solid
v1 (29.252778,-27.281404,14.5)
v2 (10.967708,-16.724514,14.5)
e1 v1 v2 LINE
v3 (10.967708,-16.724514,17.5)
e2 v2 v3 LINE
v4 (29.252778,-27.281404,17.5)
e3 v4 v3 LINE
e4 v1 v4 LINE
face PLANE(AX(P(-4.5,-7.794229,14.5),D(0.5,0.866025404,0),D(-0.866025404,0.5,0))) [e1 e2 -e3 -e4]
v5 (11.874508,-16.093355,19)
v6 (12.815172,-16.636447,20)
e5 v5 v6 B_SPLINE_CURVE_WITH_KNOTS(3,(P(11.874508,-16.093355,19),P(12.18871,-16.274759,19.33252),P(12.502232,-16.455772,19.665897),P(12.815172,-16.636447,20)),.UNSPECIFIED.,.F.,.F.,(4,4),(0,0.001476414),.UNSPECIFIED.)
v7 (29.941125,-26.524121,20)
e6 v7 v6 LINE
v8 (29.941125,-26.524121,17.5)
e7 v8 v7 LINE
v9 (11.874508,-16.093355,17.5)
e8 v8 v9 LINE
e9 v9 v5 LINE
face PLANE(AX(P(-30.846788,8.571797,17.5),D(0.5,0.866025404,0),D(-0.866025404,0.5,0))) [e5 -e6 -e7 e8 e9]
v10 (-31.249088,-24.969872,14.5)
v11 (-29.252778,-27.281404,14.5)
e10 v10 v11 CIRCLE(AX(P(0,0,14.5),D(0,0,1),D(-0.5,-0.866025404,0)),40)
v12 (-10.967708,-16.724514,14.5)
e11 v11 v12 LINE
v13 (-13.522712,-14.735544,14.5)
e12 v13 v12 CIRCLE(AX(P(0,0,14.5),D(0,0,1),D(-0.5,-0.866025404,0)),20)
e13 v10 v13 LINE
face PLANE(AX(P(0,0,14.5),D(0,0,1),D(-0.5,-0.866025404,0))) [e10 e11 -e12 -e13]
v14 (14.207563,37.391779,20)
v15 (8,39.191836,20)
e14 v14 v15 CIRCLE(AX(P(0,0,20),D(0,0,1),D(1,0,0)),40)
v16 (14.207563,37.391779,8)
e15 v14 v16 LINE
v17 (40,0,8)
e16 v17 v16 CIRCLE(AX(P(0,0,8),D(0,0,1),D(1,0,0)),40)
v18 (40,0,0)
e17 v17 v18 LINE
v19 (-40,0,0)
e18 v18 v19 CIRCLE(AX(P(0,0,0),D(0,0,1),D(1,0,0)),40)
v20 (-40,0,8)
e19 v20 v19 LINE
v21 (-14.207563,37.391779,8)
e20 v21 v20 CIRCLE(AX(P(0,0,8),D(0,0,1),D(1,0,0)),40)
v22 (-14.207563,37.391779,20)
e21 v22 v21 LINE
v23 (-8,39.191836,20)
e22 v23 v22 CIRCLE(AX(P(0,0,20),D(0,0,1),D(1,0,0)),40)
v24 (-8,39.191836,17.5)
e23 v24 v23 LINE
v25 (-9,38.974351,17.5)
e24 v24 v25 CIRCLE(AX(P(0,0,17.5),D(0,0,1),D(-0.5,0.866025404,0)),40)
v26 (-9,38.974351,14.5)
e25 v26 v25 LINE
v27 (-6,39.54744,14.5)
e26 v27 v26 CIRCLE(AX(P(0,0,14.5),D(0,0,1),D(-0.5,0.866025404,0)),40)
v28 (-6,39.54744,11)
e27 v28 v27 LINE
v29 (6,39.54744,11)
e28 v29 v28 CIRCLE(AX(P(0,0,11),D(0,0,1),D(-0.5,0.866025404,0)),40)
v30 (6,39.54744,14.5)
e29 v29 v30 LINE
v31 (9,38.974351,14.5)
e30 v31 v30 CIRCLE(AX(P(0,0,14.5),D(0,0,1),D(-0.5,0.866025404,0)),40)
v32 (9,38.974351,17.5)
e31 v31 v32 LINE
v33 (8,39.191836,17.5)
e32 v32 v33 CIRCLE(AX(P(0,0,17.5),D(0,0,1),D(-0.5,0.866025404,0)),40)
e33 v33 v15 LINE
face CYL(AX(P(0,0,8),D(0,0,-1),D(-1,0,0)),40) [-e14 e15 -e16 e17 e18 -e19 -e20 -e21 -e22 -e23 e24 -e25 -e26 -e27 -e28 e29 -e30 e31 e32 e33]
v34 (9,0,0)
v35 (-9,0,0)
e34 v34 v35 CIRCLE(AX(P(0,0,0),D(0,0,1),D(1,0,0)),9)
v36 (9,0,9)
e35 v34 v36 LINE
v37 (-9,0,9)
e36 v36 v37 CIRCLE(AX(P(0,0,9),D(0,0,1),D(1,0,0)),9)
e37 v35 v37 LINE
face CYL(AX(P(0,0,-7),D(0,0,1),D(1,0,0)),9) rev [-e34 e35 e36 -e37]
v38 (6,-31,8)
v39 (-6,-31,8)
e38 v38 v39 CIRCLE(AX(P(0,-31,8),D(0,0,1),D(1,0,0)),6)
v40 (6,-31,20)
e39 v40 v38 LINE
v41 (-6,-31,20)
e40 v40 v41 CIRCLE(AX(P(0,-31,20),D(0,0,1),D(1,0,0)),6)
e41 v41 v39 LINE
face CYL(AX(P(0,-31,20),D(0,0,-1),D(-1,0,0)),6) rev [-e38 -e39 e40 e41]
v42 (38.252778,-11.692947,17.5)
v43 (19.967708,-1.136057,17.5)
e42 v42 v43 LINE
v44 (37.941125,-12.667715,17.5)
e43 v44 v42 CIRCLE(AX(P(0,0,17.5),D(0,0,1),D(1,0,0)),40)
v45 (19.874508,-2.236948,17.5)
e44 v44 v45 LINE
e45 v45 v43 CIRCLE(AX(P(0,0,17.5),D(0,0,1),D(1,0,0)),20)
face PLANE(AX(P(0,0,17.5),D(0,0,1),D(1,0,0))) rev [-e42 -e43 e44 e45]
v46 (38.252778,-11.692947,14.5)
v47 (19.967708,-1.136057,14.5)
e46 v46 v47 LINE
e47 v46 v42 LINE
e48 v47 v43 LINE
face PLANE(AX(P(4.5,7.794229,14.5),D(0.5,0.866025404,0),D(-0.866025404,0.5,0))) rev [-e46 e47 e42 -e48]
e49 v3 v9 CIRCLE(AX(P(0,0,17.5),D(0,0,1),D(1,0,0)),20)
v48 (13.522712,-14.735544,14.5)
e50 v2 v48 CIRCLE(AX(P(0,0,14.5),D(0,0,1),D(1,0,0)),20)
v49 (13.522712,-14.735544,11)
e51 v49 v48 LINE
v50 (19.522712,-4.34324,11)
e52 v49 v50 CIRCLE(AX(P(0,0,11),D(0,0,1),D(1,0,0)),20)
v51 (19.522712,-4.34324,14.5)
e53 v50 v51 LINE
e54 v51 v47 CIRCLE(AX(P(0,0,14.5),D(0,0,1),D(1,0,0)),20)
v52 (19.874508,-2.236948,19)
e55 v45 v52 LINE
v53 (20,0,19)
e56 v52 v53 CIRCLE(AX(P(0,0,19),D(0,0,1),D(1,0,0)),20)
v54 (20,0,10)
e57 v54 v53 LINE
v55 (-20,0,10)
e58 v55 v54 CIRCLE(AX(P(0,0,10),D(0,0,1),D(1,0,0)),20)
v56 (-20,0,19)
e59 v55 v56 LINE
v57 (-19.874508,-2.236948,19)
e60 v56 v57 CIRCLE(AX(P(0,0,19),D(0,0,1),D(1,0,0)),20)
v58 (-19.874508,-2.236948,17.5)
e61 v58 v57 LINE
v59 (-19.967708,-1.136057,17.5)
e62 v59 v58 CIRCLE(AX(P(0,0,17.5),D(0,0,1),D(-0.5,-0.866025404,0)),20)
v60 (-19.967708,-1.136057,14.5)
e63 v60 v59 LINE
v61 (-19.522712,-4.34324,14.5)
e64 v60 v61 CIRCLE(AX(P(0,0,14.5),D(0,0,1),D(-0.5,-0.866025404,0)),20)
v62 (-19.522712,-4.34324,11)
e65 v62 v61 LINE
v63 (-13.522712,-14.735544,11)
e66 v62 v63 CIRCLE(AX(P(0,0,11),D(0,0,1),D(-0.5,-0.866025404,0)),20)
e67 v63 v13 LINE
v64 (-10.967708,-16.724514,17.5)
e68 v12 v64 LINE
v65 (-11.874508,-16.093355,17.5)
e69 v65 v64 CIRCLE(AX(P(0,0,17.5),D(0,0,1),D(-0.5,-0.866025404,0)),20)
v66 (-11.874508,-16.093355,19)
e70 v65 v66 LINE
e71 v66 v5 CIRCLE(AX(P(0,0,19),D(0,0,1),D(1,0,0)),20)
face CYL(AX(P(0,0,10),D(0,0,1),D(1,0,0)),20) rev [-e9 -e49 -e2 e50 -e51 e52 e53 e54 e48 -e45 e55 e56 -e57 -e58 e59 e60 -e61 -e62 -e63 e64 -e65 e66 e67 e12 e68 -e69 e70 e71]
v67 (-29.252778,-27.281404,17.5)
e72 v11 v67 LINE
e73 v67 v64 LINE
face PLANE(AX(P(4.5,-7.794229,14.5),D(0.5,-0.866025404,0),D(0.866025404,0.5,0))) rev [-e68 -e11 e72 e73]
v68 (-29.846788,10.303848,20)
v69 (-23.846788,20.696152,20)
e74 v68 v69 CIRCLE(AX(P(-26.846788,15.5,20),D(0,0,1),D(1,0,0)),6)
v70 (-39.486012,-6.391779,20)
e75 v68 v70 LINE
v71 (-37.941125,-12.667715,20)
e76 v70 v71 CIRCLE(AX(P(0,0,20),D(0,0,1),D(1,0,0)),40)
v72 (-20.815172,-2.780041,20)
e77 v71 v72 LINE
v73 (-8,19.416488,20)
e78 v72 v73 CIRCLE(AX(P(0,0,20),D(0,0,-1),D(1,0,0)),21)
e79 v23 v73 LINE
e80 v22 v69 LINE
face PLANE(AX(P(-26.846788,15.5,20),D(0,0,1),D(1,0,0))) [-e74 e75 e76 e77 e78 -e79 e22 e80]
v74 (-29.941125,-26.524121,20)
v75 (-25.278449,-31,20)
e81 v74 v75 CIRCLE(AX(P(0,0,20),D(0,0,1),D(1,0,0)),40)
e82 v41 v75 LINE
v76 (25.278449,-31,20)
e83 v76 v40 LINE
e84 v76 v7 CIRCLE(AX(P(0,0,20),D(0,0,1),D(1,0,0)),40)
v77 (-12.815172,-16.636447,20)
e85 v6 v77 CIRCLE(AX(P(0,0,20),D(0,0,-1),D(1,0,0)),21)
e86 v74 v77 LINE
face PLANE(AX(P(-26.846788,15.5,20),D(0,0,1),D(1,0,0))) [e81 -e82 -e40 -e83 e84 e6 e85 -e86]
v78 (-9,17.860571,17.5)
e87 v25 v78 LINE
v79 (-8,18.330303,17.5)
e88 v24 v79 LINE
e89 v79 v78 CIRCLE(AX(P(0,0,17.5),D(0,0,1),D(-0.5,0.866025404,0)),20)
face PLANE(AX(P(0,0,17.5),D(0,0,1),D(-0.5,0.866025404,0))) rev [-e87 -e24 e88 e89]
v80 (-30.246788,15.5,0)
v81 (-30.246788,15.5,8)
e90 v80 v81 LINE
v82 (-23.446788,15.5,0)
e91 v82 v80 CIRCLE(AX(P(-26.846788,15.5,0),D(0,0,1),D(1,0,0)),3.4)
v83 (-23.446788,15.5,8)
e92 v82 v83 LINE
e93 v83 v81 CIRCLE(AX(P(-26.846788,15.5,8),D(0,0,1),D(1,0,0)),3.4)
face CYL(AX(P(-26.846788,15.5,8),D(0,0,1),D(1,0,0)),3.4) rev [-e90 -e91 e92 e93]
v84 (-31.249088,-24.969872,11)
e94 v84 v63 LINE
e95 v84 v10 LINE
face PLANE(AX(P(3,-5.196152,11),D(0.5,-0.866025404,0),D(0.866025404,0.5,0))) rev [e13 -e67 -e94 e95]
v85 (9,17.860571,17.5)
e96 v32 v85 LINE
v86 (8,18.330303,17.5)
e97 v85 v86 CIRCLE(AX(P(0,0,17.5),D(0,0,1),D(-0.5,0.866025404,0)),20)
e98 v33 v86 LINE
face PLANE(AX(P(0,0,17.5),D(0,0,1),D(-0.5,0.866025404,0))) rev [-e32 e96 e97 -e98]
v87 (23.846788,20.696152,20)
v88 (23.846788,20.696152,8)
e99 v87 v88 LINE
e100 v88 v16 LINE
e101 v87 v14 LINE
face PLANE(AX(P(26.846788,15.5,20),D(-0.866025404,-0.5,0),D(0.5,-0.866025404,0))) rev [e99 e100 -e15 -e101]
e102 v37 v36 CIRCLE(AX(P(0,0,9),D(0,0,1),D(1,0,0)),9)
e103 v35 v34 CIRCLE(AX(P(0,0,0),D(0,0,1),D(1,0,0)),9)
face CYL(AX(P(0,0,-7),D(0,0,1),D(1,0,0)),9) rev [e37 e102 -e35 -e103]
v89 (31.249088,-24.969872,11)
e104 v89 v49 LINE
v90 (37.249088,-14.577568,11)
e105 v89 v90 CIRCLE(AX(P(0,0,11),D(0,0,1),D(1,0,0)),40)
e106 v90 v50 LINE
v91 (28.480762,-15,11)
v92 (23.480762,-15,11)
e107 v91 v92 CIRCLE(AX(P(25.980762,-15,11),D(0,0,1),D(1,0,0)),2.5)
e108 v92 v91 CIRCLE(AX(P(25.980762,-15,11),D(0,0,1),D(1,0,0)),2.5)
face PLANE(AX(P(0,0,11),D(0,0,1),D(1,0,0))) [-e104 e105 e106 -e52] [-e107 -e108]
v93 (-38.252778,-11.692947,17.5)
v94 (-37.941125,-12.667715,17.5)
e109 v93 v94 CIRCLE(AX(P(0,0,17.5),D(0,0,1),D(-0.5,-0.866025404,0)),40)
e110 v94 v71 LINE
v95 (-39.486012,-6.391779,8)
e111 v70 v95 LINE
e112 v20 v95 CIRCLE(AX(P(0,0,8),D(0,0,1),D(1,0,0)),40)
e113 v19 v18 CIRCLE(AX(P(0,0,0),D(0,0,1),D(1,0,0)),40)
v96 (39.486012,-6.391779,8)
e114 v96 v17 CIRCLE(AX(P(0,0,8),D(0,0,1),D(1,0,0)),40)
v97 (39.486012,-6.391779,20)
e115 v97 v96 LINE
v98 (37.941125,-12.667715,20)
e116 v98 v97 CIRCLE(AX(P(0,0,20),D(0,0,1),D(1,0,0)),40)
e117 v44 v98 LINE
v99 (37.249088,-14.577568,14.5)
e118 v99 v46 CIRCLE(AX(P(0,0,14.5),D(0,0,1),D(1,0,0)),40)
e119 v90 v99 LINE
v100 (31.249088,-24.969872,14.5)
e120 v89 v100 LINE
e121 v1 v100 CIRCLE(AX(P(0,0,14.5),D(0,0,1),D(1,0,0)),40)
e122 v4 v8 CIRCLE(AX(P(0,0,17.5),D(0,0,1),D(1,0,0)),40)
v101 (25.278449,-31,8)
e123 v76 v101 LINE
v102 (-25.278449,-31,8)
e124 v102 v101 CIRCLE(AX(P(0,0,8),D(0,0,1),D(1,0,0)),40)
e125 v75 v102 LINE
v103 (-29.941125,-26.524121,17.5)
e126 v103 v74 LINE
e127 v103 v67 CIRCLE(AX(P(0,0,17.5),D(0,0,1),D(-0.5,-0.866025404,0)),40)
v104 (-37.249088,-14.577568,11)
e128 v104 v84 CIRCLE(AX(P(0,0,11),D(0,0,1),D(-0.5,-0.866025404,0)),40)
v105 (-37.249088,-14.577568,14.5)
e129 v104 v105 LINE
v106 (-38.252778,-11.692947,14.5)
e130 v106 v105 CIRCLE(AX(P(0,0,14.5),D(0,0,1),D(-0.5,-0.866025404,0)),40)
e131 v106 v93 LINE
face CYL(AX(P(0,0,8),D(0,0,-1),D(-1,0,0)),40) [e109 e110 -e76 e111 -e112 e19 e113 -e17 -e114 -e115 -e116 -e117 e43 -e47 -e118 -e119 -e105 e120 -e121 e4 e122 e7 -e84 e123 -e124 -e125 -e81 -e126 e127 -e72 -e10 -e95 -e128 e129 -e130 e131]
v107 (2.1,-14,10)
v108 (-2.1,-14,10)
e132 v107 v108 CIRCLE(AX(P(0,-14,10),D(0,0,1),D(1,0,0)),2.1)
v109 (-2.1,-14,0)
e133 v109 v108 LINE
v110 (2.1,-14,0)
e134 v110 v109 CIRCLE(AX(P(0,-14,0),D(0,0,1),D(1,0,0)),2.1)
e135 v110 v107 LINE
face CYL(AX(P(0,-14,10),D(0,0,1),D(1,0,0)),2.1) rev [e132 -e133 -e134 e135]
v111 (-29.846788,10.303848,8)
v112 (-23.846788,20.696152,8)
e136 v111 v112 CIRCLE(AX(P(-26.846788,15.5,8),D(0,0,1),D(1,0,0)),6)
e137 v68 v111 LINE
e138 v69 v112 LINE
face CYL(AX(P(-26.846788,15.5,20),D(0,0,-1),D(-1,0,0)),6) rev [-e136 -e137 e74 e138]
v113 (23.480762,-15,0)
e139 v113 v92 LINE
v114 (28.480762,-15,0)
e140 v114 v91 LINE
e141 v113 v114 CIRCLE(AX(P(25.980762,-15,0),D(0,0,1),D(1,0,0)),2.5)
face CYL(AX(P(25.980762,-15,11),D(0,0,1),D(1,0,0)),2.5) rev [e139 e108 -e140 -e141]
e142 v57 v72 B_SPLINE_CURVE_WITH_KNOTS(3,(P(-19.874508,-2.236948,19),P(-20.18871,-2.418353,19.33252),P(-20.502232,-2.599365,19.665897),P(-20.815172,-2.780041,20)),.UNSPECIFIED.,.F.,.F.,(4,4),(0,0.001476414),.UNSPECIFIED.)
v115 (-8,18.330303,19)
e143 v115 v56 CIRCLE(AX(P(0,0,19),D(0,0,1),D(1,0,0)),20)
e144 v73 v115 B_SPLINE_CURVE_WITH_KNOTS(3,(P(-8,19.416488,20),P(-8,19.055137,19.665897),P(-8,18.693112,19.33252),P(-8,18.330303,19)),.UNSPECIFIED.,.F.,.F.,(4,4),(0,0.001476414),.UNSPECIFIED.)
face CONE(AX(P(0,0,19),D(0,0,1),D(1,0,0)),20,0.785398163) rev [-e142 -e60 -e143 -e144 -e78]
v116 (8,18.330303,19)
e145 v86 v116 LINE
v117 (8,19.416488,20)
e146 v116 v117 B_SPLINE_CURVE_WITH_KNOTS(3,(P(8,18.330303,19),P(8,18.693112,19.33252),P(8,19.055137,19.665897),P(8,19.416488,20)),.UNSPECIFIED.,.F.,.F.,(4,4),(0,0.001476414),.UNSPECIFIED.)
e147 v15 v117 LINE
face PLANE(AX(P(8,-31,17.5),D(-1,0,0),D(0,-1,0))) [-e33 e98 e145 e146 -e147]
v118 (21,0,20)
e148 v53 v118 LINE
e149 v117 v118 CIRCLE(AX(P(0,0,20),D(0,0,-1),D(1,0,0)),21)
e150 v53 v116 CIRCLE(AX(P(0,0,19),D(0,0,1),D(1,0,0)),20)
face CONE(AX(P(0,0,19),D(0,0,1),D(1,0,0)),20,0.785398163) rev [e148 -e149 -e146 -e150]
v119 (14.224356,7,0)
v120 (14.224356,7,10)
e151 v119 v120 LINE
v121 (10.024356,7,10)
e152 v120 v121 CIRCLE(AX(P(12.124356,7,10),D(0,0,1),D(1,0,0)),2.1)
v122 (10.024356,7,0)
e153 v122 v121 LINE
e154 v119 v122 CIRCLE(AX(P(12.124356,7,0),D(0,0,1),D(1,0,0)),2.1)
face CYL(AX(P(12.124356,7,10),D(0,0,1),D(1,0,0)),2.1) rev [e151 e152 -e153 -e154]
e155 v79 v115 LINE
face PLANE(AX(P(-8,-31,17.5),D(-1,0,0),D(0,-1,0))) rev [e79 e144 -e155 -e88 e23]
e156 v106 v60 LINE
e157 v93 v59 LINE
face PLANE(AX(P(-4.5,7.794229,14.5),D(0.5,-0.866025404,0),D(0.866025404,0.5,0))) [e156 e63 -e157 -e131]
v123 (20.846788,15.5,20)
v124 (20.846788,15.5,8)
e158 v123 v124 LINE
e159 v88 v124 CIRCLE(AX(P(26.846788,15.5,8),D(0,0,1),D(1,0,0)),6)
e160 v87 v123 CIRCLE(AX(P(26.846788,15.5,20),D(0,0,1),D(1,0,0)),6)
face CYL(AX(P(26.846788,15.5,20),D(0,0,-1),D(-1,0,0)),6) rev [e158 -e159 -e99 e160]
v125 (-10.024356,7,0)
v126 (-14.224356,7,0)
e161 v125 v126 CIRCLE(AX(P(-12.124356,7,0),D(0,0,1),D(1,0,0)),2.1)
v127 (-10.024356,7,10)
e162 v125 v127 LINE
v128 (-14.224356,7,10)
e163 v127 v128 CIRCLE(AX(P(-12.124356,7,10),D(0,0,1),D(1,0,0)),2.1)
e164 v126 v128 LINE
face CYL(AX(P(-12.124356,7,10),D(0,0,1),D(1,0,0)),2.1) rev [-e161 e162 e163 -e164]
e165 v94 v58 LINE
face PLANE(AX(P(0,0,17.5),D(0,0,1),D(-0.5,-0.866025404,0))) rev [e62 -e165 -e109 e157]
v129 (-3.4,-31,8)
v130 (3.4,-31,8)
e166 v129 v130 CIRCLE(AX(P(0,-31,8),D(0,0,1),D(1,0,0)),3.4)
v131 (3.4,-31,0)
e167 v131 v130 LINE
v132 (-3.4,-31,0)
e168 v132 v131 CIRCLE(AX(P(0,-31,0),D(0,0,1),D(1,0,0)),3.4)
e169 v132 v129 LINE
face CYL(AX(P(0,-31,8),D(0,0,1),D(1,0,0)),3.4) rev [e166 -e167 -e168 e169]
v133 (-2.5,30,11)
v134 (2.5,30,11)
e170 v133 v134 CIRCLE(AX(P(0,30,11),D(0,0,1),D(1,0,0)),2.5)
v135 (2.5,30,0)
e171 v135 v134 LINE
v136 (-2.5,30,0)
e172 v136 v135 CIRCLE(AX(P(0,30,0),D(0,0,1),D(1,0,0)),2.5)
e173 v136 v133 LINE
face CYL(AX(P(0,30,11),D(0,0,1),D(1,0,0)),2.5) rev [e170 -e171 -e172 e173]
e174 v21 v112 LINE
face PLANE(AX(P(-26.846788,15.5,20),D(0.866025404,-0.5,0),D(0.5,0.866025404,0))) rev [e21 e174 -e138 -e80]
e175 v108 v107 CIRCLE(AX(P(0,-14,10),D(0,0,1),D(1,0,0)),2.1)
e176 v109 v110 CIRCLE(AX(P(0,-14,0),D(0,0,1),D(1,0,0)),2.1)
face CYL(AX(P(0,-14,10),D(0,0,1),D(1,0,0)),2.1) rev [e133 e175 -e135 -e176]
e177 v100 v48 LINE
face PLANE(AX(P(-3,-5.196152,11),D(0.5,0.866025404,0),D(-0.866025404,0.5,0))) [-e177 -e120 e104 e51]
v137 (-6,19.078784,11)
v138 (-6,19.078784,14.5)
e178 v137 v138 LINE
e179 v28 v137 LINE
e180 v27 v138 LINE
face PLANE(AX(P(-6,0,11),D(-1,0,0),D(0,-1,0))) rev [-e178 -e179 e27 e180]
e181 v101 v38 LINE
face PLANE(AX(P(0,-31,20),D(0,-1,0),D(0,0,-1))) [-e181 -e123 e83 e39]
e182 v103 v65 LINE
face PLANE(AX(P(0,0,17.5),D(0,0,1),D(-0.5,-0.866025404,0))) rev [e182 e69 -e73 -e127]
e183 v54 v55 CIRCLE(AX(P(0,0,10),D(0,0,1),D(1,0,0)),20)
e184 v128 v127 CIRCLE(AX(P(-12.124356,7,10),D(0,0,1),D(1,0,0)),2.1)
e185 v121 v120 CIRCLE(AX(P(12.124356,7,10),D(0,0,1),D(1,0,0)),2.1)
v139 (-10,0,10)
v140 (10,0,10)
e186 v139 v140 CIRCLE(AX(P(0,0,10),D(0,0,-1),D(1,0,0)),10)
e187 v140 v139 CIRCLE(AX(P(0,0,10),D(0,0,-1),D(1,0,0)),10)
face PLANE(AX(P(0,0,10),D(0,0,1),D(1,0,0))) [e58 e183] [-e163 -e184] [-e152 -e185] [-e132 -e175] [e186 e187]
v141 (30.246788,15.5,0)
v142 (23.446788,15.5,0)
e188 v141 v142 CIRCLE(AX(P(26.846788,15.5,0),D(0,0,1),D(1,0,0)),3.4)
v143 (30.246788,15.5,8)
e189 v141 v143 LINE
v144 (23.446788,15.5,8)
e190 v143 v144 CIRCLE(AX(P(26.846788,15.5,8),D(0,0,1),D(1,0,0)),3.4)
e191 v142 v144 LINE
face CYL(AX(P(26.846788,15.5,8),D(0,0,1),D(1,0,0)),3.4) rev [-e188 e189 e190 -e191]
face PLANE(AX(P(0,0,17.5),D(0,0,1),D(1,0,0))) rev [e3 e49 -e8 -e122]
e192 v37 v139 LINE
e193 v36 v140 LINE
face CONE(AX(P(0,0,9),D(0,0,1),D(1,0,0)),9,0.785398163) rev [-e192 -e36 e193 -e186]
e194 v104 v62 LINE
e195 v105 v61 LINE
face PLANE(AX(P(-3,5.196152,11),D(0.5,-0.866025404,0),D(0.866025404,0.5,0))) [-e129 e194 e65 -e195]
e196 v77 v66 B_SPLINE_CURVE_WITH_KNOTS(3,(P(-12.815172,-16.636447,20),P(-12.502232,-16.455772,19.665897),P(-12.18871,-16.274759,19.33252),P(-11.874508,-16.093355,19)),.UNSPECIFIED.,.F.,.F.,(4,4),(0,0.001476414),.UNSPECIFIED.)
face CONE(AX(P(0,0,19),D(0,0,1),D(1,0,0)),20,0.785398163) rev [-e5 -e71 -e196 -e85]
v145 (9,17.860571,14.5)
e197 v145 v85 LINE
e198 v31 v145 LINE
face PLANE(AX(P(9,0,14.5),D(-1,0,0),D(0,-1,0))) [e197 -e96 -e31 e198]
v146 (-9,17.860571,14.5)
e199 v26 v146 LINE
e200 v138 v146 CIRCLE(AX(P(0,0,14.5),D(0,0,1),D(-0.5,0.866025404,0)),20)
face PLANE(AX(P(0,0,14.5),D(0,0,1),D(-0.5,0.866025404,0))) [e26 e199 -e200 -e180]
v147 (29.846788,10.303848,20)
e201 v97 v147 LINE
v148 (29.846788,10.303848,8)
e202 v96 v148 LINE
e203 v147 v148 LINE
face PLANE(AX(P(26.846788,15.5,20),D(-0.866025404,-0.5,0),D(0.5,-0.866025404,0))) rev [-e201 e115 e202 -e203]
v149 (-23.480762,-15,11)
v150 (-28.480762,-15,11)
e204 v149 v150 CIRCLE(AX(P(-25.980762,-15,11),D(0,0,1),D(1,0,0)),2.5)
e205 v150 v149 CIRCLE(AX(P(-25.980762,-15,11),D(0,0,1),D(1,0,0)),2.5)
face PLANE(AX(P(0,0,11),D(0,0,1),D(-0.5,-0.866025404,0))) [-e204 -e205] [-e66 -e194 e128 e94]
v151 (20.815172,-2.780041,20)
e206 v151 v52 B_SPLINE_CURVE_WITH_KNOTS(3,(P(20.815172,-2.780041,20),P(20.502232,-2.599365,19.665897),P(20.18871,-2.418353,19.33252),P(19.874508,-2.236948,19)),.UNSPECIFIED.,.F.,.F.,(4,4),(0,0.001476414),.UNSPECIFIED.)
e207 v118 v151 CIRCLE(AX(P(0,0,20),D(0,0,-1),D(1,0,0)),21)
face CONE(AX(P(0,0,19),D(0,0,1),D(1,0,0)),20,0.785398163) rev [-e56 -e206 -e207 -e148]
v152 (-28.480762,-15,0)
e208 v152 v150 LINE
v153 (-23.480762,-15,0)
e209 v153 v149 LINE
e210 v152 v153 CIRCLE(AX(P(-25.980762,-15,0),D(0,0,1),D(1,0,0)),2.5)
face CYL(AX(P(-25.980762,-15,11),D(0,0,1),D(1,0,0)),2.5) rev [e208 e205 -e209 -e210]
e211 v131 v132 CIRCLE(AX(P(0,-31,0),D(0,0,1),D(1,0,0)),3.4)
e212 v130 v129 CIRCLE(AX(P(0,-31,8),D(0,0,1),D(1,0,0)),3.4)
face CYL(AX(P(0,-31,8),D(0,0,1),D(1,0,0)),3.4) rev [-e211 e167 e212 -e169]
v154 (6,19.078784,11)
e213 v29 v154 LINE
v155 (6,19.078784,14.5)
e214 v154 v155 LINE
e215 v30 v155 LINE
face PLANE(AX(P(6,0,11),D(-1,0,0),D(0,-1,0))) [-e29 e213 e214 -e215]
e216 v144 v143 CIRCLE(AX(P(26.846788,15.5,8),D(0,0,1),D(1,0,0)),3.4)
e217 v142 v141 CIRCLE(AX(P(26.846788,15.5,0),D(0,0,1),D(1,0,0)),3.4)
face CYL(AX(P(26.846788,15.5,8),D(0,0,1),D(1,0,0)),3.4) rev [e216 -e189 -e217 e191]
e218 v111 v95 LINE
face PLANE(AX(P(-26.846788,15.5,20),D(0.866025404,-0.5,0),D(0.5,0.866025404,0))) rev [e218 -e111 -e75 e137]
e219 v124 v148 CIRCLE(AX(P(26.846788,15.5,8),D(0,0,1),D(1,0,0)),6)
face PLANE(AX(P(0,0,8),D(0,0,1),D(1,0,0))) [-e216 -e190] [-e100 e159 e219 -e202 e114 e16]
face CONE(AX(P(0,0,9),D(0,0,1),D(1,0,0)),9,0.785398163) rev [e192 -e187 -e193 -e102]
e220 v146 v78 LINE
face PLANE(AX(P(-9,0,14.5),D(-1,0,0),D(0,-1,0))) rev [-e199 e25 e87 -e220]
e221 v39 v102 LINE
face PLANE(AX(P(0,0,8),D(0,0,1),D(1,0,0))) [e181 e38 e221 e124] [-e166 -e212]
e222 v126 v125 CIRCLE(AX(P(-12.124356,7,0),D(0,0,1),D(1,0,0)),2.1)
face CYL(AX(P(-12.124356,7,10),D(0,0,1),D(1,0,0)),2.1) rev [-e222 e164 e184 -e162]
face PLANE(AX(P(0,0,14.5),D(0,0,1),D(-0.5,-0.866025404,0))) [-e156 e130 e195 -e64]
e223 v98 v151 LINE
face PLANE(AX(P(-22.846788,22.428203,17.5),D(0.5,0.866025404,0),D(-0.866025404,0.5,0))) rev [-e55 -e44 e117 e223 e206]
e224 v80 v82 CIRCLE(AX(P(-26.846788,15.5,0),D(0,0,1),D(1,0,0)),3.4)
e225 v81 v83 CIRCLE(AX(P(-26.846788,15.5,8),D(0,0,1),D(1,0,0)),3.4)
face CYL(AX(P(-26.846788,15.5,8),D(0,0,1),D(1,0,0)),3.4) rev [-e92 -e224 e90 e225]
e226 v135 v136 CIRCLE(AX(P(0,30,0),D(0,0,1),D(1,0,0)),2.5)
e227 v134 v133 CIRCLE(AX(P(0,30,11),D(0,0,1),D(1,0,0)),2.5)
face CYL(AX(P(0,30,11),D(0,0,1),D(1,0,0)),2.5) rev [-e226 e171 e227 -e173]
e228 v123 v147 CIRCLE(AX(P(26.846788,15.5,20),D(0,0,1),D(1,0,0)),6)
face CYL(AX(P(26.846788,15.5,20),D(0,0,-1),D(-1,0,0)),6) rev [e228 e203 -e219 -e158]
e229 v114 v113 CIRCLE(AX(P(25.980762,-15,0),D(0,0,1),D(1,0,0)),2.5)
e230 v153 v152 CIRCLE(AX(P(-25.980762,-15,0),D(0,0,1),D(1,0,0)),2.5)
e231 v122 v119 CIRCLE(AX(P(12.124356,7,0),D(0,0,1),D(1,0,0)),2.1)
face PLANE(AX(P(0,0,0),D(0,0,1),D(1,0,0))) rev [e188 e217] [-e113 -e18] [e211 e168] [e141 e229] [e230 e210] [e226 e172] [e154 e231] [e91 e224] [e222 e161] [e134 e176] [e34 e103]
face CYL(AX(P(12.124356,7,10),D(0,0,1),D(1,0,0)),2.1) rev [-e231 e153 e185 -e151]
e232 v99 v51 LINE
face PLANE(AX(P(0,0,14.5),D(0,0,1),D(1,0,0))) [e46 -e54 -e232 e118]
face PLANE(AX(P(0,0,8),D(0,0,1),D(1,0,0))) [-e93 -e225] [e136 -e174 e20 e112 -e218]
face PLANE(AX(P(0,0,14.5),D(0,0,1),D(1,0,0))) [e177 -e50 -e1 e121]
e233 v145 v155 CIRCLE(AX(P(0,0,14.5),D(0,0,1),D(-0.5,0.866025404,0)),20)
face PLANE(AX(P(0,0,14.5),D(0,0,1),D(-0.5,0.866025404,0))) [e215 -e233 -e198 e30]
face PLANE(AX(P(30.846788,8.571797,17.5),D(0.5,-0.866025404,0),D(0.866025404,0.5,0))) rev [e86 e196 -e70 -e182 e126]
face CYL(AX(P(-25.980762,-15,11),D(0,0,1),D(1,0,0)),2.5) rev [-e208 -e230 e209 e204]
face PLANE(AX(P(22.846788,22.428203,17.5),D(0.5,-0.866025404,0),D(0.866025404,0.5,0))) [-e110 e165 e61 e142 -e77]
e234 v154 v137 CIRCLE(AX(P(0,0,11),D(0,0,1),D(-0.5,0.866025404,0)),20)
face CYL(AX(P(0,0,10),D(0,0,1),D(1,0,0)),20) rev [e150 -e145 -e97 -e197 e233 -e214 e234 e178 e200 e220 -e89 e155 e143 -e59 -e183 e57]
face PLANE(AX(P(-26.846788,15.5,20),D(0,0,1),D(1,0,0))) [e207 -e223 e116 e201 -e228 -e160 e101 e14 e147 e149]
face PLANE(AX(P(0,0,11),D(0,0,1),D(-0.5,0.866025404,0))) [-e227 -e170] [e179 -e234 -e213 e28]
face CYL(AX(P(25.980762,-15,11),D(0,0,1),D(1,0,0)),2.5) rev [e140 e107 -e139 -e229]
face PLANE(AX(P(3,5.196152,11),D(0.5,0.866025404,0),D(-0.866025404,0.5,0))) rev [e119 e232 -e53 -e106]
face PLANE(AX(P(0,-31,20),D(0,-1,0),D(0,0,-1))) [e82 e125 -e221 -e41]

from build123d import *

# Parameters (mm, degrees)
FLANGE_AND_SPOKE_PROFILE_SKETCH_R = 40
FLANGE_DISC_80_DEPTH              = 8
SPOKES_START                      = 8
SPOKES_3X_DEPTH                   = 12
CENTRE_RECESS_SKETCH_40_R         = 20
CENTRE_RECESS_40_DEPTH            = 10
LOCKING_START                     = 17.5
LOCKING_SLOT_STEP_2_5MM_DEPTH     = 2.5
LOCKING_START_2                   = 14.5
LOCKING_SLOT_STEP_3MM_DEPTH       = 3
LOCKING_START_3                   = 11
LOCKING_SLOT_STEP_3_5MM_DEPTH     = 3.5
LOCKING_SLOT_PATTERN_3X_COUNT     = 3
BORE_SKETCH_18_R                  = 9
BORE_18_DEPTH                     = 17
TAPPED_HOLES_3XM5_PCD28_D         = 4.2
TAPPED_HOLES_3XM6_PCD60_D         = 5
TAPPED_HOLES_3XM8_PCD62_D         = 6.8
EDGE_CHAMFER_1X45_SIZE            = 1


with BuildPart() as part:
    # Flange and Spoke Profile Sketch → Flange Disc _80 (new body)
    with BuildSketch(Plane.XY):
        Circle(FLANGE_AND_SPOKE_PROFILE_SKETCH_R)
    extrude(amount=FLANGE_DISC_80_DEPTH)

    # Sketch1_3 → Spokes 3x (add)
    with BuildSketch(Plane.XY.offset(SPOKES_START)):
        with BuildLine():
            Line((-29.846787517, 10.303847577), (-39.486012177, -6.391779279))
            ThreePointArc((-39.486012177, -6.391779279), (-34.641016151, -20), (-25.27844932, -31))
            Line((-25.27844932, -31), (-6, -31))
            ThreePointArc((-6, -31), (0, -25), (6, -31))
            Line((6, -31), (25.27844932, -31))
            ThreePointArc((25.27844932, -31), (34.641016151, -20), (39.486012177, -6.391779279))
            Line((39.486012177, -6.391779279), (29.846787517, 10.303847577))
            ThreePointArc((29.846787517, 10.303847577), (21.650635095, 12.5), (23.846787517, 20.696152423))
            Line((23.846787517, 20.696152423), (14.207562858, 37.391779279))
            ThreePointArc((14.207562858, 37.391779279), (0, 40), (-14.207562858, 37.391779279))
            Line((-14.207562858, 37.391779279), (-23.846787517, 20.696152423))
            ThreePointArc((-23.846787517, 20.696152423), (-21.650635095, 12.5), (-29.846787517, 10.303847577))
        make_face()
    extrude(amount=SPOKES_3X_DEPTH)

    # Centre Recess Sketch _40 → Centre Recess _40 (cut)
    with BuildSketch(Plane.XY.offset(20)):
        Circle(CENTRE_RECESS_SKETCH_40_R)
    extrude(amount=-CENTRE_RECESS_40_DEPTH, mode=Mode.SUBTRACT)

    # Locking Slot Sketch → Locking Slot Step 2.5mm (cut)
    with BuildSketch(Plane.XY.offset(LOCKING_START)):
        with BuildLine():
            Line((37.249087579, -14.577567511), (19.522711642, -4.343239591))
            ThreePointArc((19.522711642, -4.343239591), (17.320508076, -10), (13.522711642, -14.735544437))
            Line((13.522711642, -14.735544437), (31.249087579, -24.969872356))
            ThreePointArc((31.249087579, -24.969872356), (34.641016151, -20), (37.249087579, -14.577567511))
        make_face()
        with BuildLine():
            Line((31.249087579, -24.969872356), (13.522711642, -14.735544437))
            ThreePointArc((13.522711642, -14.735544437), (12.716744938, -15.436463267), (11.874507866, -16.09335462))
            Line((11.874507866, -16.09335462), (29.941125497, -26.524121173))
            ThreePointArc((29.941125497, -26.524121173), (30.604974537, -25.755301077), (31.249087579, -24.969872356))
        make_face()
        with BuildLine():
            ThreePointArc((19.874507866, -2.23694816), (19.726741803, -3.294792536), (19.522711642, -4.343239591))
            Line((19.522711642, -4.343239591), (37.249087579, -14.577567511))
            ThreePointArc((37.249087579, -14.577567511), (37.607232284, -13.627034893), (37.941125497, -12.667714712))
            Line((37.941125497, -12.667714712), (19.874507866, -2.23694816))
        make_face()
    locking_slot_step_2_5mm = extrude(amount=LOCKING_SLOT_STEP_2_5MM_DEPTH, mode=Mode.SUBTRACT)

    # Sketch5_3 → Locking Slot Step 3mm (cut)
    with BuildSketch(Plane.XY.offset(LOCKING_START_2)):
        with BuildLine():
            Line((37.249087579, -14.577567511), (19.522711642, -4.343239591))
            ThreePointArc((19.522711642, -4.343239591), (17.320508076, -10), (13.522711642, -14.735544437))
            Line((13.522711642, -14.735544437), (31.249087579, -24.969872356))
            ThreePointArc((31.249087579, -24.969872356), (34.641016151, -20), (37.249087579, -14.577567511))
        make_face()
        with BuildLine():
            ThreePointArc((19.874507866, -2.23694816), (19.726741803, -3.294792536), (19.522711642, -4.343239591))
            Line((19.522711642, -4.343239591), (37.249087579, -14.577567511))
            ThreePointArc((37.249087579, -14.577567511), (37.607232284, -13.627034893), (37.941125497, -12.667714712))
            Line((37.941125497, -12.667714712), (19.874507866, -2.23694816))
        make_face()
        with BuildLine():
            ThreePointArc((19.967708298, -1.136056916), (19.928711389, -1.687146227), (19.874507866, -2.23694816))
            Line((19.874507866, -2.23694816), (37.941125497, -12.667714712))
            ThreePointArc((37.941125497, -12.667714712), (38.100069067, -12.181327395), (38.252777663, -11.692946636))
            Line((38.252777663, -11.692946636), (19.967708298, -1.136056916))
        make_face()
        with BuildLine():
            Line((31.249087579, -24.969872356), (13.522711642, -14.735544437))
            ThreePointArc((13.522711642, -14.735544437), (12.716744938, -15.436463267), (11.874507866, -16.09335462))
            Line((11.874507866, -16.09335462), (29.941125497, -26.524121173))
            ThreePointArc((29.941125497, -26.524121173), (30.604974537, -25.755301077), (31.249087579, -24.969872356))
        make_face()
        with BuildLine():
            Line((29.941125497, -26.524121173), (11.874507866, -16.09335462))
            ThreePointArc((11.874507866, -16.09335462), (11.425467186, -16.415197214), (10.967708298, -16.724514184))
            Line((10.967708298, -16.724514184), (29.252777663, -27.281403904))
            ThreePointArc((29.252777663, -27.281403904), (29.599373509, -26.904964001), (29.941125497, -26.524121173))
        make_face()
    locking_slot_step_3mm = extrude(amount=LOCKING_SLOT_STEP_3MM_DEPTH, mode=Mode.SUBTRACT)

    # Sketch5_4 → Locking Slot Step 3.5mm (cut)
    with BuildSketch(Plane.XY.offset(LOCKING_START_3)):
        with BuildLine():
            Line((37.249087579, -14.577567511), (19.522711642, -4.343239591))
            ThreePointArc((19.522711642, -4.343239591), (17.320508076, -10), (13.522711642, -14.735544437))
            Line((13.522711642, -14.735544437), (31.249087579, -24.969872356))
            ThreePointArc((31.249087579, -24.969872356), (34.641016151, -20), (37.249087579, -14.577567511))
        make_face()
    locking_slot_step_3_5mm = extrude(amount=LOCKING_SLOT_STEP_3_5MM_DEPTH, mode=Mode.SUBTRACT)

    # Locking Slot Pattern 3x: Locking Slot Step 2.5mm, Locking Slot Step 3mm, Locking Slot Step 3.5mm ×3 about axis
    locking_slot_pattern_3x_axis = Axis((0, 0, 0), (0, 0, 1))
    add([locking_slot_step_2_5mm.rotate(locking_slot_pattern_3x_axis, i * 360 / LOCKING_SLOT_PATTERN_3X_COUNT) for i in range(1, LOCKING_SLOT_PATTERN_3X_COUNT)], mode=Mode.SUBTRACT)
    add([locking_slot_step_3mm.rotate(locking_slot_pattern_3x_axis, i * 360 / LOCKING_SLOT_PATTERN_3X_COUNT) for i in range(1, LOCKING_SLOT_PATTERN_3X_COUNT)], mode=Mode.SUBTRACT)
    add([locking_slot_step_3_5mm.rotate(locking_slot_pattern_3x_axis, i * 360 / LOCKING_SLOT_PATTERN_3X_COUNT) for i in range(1, LOCKING_SLOT_PATTERN_3X_COUNT)], mode=Mode.SUBTRACT)

    # Bore Sketch _18 → Bore _18 (cut)
    with BuildSketch(Plane.XY.offset(10)):
        Circle(BORE_SKETCH_18_R)
    extrude(amount=-BORE_18_DEPTH, mode=Mode.SUBTRACT)

    # Tapped Holes 3xM5 PCD28 (through all)
    with Locations(Plane.XY.offset(10)):
        with Locations((12.124355653, 7), (0, -14), (-12.124355653, 7)):
            Hole(TAPPED_HOLES_3XM5_PCD28_D / 2)

    # Tapped Holes 3xM6 PCD60 (through all)
    with Locations(Plane.XY.offset(11)):
        with Locations((-25.980762114, -15), (0, 30), (25.980762114, -15)):
            Hole(TAPPED_HOLES_3XM6_PCD60_D / 2)

    # Tapped Holes 3xM8 PCD62 (through all)
    with Locations(Plane.XY.offset(8)):
        with Locations((26.846787517, 15.5), (0, -31), (-26.846787517, 15.5)):
            Hole(TAPPED_HOLES_3XM8_PCD62_D / 2)

    # Edge Chamfer 1x45
    edge_chamfer_1x45_edges = [part.edges().sort_by_distance(p)[0] for p in [
        (-17.320508076, 10, 20),
        (0, -20, 20),
        (-9, 0, 10),
        (16.733200531, 10.95445115, 20),
    ]]
    chamfer(edge_chamfer_1x45_edges, length=EDGE_CHAMFER_1X45_SIZE)


solid = part.part
